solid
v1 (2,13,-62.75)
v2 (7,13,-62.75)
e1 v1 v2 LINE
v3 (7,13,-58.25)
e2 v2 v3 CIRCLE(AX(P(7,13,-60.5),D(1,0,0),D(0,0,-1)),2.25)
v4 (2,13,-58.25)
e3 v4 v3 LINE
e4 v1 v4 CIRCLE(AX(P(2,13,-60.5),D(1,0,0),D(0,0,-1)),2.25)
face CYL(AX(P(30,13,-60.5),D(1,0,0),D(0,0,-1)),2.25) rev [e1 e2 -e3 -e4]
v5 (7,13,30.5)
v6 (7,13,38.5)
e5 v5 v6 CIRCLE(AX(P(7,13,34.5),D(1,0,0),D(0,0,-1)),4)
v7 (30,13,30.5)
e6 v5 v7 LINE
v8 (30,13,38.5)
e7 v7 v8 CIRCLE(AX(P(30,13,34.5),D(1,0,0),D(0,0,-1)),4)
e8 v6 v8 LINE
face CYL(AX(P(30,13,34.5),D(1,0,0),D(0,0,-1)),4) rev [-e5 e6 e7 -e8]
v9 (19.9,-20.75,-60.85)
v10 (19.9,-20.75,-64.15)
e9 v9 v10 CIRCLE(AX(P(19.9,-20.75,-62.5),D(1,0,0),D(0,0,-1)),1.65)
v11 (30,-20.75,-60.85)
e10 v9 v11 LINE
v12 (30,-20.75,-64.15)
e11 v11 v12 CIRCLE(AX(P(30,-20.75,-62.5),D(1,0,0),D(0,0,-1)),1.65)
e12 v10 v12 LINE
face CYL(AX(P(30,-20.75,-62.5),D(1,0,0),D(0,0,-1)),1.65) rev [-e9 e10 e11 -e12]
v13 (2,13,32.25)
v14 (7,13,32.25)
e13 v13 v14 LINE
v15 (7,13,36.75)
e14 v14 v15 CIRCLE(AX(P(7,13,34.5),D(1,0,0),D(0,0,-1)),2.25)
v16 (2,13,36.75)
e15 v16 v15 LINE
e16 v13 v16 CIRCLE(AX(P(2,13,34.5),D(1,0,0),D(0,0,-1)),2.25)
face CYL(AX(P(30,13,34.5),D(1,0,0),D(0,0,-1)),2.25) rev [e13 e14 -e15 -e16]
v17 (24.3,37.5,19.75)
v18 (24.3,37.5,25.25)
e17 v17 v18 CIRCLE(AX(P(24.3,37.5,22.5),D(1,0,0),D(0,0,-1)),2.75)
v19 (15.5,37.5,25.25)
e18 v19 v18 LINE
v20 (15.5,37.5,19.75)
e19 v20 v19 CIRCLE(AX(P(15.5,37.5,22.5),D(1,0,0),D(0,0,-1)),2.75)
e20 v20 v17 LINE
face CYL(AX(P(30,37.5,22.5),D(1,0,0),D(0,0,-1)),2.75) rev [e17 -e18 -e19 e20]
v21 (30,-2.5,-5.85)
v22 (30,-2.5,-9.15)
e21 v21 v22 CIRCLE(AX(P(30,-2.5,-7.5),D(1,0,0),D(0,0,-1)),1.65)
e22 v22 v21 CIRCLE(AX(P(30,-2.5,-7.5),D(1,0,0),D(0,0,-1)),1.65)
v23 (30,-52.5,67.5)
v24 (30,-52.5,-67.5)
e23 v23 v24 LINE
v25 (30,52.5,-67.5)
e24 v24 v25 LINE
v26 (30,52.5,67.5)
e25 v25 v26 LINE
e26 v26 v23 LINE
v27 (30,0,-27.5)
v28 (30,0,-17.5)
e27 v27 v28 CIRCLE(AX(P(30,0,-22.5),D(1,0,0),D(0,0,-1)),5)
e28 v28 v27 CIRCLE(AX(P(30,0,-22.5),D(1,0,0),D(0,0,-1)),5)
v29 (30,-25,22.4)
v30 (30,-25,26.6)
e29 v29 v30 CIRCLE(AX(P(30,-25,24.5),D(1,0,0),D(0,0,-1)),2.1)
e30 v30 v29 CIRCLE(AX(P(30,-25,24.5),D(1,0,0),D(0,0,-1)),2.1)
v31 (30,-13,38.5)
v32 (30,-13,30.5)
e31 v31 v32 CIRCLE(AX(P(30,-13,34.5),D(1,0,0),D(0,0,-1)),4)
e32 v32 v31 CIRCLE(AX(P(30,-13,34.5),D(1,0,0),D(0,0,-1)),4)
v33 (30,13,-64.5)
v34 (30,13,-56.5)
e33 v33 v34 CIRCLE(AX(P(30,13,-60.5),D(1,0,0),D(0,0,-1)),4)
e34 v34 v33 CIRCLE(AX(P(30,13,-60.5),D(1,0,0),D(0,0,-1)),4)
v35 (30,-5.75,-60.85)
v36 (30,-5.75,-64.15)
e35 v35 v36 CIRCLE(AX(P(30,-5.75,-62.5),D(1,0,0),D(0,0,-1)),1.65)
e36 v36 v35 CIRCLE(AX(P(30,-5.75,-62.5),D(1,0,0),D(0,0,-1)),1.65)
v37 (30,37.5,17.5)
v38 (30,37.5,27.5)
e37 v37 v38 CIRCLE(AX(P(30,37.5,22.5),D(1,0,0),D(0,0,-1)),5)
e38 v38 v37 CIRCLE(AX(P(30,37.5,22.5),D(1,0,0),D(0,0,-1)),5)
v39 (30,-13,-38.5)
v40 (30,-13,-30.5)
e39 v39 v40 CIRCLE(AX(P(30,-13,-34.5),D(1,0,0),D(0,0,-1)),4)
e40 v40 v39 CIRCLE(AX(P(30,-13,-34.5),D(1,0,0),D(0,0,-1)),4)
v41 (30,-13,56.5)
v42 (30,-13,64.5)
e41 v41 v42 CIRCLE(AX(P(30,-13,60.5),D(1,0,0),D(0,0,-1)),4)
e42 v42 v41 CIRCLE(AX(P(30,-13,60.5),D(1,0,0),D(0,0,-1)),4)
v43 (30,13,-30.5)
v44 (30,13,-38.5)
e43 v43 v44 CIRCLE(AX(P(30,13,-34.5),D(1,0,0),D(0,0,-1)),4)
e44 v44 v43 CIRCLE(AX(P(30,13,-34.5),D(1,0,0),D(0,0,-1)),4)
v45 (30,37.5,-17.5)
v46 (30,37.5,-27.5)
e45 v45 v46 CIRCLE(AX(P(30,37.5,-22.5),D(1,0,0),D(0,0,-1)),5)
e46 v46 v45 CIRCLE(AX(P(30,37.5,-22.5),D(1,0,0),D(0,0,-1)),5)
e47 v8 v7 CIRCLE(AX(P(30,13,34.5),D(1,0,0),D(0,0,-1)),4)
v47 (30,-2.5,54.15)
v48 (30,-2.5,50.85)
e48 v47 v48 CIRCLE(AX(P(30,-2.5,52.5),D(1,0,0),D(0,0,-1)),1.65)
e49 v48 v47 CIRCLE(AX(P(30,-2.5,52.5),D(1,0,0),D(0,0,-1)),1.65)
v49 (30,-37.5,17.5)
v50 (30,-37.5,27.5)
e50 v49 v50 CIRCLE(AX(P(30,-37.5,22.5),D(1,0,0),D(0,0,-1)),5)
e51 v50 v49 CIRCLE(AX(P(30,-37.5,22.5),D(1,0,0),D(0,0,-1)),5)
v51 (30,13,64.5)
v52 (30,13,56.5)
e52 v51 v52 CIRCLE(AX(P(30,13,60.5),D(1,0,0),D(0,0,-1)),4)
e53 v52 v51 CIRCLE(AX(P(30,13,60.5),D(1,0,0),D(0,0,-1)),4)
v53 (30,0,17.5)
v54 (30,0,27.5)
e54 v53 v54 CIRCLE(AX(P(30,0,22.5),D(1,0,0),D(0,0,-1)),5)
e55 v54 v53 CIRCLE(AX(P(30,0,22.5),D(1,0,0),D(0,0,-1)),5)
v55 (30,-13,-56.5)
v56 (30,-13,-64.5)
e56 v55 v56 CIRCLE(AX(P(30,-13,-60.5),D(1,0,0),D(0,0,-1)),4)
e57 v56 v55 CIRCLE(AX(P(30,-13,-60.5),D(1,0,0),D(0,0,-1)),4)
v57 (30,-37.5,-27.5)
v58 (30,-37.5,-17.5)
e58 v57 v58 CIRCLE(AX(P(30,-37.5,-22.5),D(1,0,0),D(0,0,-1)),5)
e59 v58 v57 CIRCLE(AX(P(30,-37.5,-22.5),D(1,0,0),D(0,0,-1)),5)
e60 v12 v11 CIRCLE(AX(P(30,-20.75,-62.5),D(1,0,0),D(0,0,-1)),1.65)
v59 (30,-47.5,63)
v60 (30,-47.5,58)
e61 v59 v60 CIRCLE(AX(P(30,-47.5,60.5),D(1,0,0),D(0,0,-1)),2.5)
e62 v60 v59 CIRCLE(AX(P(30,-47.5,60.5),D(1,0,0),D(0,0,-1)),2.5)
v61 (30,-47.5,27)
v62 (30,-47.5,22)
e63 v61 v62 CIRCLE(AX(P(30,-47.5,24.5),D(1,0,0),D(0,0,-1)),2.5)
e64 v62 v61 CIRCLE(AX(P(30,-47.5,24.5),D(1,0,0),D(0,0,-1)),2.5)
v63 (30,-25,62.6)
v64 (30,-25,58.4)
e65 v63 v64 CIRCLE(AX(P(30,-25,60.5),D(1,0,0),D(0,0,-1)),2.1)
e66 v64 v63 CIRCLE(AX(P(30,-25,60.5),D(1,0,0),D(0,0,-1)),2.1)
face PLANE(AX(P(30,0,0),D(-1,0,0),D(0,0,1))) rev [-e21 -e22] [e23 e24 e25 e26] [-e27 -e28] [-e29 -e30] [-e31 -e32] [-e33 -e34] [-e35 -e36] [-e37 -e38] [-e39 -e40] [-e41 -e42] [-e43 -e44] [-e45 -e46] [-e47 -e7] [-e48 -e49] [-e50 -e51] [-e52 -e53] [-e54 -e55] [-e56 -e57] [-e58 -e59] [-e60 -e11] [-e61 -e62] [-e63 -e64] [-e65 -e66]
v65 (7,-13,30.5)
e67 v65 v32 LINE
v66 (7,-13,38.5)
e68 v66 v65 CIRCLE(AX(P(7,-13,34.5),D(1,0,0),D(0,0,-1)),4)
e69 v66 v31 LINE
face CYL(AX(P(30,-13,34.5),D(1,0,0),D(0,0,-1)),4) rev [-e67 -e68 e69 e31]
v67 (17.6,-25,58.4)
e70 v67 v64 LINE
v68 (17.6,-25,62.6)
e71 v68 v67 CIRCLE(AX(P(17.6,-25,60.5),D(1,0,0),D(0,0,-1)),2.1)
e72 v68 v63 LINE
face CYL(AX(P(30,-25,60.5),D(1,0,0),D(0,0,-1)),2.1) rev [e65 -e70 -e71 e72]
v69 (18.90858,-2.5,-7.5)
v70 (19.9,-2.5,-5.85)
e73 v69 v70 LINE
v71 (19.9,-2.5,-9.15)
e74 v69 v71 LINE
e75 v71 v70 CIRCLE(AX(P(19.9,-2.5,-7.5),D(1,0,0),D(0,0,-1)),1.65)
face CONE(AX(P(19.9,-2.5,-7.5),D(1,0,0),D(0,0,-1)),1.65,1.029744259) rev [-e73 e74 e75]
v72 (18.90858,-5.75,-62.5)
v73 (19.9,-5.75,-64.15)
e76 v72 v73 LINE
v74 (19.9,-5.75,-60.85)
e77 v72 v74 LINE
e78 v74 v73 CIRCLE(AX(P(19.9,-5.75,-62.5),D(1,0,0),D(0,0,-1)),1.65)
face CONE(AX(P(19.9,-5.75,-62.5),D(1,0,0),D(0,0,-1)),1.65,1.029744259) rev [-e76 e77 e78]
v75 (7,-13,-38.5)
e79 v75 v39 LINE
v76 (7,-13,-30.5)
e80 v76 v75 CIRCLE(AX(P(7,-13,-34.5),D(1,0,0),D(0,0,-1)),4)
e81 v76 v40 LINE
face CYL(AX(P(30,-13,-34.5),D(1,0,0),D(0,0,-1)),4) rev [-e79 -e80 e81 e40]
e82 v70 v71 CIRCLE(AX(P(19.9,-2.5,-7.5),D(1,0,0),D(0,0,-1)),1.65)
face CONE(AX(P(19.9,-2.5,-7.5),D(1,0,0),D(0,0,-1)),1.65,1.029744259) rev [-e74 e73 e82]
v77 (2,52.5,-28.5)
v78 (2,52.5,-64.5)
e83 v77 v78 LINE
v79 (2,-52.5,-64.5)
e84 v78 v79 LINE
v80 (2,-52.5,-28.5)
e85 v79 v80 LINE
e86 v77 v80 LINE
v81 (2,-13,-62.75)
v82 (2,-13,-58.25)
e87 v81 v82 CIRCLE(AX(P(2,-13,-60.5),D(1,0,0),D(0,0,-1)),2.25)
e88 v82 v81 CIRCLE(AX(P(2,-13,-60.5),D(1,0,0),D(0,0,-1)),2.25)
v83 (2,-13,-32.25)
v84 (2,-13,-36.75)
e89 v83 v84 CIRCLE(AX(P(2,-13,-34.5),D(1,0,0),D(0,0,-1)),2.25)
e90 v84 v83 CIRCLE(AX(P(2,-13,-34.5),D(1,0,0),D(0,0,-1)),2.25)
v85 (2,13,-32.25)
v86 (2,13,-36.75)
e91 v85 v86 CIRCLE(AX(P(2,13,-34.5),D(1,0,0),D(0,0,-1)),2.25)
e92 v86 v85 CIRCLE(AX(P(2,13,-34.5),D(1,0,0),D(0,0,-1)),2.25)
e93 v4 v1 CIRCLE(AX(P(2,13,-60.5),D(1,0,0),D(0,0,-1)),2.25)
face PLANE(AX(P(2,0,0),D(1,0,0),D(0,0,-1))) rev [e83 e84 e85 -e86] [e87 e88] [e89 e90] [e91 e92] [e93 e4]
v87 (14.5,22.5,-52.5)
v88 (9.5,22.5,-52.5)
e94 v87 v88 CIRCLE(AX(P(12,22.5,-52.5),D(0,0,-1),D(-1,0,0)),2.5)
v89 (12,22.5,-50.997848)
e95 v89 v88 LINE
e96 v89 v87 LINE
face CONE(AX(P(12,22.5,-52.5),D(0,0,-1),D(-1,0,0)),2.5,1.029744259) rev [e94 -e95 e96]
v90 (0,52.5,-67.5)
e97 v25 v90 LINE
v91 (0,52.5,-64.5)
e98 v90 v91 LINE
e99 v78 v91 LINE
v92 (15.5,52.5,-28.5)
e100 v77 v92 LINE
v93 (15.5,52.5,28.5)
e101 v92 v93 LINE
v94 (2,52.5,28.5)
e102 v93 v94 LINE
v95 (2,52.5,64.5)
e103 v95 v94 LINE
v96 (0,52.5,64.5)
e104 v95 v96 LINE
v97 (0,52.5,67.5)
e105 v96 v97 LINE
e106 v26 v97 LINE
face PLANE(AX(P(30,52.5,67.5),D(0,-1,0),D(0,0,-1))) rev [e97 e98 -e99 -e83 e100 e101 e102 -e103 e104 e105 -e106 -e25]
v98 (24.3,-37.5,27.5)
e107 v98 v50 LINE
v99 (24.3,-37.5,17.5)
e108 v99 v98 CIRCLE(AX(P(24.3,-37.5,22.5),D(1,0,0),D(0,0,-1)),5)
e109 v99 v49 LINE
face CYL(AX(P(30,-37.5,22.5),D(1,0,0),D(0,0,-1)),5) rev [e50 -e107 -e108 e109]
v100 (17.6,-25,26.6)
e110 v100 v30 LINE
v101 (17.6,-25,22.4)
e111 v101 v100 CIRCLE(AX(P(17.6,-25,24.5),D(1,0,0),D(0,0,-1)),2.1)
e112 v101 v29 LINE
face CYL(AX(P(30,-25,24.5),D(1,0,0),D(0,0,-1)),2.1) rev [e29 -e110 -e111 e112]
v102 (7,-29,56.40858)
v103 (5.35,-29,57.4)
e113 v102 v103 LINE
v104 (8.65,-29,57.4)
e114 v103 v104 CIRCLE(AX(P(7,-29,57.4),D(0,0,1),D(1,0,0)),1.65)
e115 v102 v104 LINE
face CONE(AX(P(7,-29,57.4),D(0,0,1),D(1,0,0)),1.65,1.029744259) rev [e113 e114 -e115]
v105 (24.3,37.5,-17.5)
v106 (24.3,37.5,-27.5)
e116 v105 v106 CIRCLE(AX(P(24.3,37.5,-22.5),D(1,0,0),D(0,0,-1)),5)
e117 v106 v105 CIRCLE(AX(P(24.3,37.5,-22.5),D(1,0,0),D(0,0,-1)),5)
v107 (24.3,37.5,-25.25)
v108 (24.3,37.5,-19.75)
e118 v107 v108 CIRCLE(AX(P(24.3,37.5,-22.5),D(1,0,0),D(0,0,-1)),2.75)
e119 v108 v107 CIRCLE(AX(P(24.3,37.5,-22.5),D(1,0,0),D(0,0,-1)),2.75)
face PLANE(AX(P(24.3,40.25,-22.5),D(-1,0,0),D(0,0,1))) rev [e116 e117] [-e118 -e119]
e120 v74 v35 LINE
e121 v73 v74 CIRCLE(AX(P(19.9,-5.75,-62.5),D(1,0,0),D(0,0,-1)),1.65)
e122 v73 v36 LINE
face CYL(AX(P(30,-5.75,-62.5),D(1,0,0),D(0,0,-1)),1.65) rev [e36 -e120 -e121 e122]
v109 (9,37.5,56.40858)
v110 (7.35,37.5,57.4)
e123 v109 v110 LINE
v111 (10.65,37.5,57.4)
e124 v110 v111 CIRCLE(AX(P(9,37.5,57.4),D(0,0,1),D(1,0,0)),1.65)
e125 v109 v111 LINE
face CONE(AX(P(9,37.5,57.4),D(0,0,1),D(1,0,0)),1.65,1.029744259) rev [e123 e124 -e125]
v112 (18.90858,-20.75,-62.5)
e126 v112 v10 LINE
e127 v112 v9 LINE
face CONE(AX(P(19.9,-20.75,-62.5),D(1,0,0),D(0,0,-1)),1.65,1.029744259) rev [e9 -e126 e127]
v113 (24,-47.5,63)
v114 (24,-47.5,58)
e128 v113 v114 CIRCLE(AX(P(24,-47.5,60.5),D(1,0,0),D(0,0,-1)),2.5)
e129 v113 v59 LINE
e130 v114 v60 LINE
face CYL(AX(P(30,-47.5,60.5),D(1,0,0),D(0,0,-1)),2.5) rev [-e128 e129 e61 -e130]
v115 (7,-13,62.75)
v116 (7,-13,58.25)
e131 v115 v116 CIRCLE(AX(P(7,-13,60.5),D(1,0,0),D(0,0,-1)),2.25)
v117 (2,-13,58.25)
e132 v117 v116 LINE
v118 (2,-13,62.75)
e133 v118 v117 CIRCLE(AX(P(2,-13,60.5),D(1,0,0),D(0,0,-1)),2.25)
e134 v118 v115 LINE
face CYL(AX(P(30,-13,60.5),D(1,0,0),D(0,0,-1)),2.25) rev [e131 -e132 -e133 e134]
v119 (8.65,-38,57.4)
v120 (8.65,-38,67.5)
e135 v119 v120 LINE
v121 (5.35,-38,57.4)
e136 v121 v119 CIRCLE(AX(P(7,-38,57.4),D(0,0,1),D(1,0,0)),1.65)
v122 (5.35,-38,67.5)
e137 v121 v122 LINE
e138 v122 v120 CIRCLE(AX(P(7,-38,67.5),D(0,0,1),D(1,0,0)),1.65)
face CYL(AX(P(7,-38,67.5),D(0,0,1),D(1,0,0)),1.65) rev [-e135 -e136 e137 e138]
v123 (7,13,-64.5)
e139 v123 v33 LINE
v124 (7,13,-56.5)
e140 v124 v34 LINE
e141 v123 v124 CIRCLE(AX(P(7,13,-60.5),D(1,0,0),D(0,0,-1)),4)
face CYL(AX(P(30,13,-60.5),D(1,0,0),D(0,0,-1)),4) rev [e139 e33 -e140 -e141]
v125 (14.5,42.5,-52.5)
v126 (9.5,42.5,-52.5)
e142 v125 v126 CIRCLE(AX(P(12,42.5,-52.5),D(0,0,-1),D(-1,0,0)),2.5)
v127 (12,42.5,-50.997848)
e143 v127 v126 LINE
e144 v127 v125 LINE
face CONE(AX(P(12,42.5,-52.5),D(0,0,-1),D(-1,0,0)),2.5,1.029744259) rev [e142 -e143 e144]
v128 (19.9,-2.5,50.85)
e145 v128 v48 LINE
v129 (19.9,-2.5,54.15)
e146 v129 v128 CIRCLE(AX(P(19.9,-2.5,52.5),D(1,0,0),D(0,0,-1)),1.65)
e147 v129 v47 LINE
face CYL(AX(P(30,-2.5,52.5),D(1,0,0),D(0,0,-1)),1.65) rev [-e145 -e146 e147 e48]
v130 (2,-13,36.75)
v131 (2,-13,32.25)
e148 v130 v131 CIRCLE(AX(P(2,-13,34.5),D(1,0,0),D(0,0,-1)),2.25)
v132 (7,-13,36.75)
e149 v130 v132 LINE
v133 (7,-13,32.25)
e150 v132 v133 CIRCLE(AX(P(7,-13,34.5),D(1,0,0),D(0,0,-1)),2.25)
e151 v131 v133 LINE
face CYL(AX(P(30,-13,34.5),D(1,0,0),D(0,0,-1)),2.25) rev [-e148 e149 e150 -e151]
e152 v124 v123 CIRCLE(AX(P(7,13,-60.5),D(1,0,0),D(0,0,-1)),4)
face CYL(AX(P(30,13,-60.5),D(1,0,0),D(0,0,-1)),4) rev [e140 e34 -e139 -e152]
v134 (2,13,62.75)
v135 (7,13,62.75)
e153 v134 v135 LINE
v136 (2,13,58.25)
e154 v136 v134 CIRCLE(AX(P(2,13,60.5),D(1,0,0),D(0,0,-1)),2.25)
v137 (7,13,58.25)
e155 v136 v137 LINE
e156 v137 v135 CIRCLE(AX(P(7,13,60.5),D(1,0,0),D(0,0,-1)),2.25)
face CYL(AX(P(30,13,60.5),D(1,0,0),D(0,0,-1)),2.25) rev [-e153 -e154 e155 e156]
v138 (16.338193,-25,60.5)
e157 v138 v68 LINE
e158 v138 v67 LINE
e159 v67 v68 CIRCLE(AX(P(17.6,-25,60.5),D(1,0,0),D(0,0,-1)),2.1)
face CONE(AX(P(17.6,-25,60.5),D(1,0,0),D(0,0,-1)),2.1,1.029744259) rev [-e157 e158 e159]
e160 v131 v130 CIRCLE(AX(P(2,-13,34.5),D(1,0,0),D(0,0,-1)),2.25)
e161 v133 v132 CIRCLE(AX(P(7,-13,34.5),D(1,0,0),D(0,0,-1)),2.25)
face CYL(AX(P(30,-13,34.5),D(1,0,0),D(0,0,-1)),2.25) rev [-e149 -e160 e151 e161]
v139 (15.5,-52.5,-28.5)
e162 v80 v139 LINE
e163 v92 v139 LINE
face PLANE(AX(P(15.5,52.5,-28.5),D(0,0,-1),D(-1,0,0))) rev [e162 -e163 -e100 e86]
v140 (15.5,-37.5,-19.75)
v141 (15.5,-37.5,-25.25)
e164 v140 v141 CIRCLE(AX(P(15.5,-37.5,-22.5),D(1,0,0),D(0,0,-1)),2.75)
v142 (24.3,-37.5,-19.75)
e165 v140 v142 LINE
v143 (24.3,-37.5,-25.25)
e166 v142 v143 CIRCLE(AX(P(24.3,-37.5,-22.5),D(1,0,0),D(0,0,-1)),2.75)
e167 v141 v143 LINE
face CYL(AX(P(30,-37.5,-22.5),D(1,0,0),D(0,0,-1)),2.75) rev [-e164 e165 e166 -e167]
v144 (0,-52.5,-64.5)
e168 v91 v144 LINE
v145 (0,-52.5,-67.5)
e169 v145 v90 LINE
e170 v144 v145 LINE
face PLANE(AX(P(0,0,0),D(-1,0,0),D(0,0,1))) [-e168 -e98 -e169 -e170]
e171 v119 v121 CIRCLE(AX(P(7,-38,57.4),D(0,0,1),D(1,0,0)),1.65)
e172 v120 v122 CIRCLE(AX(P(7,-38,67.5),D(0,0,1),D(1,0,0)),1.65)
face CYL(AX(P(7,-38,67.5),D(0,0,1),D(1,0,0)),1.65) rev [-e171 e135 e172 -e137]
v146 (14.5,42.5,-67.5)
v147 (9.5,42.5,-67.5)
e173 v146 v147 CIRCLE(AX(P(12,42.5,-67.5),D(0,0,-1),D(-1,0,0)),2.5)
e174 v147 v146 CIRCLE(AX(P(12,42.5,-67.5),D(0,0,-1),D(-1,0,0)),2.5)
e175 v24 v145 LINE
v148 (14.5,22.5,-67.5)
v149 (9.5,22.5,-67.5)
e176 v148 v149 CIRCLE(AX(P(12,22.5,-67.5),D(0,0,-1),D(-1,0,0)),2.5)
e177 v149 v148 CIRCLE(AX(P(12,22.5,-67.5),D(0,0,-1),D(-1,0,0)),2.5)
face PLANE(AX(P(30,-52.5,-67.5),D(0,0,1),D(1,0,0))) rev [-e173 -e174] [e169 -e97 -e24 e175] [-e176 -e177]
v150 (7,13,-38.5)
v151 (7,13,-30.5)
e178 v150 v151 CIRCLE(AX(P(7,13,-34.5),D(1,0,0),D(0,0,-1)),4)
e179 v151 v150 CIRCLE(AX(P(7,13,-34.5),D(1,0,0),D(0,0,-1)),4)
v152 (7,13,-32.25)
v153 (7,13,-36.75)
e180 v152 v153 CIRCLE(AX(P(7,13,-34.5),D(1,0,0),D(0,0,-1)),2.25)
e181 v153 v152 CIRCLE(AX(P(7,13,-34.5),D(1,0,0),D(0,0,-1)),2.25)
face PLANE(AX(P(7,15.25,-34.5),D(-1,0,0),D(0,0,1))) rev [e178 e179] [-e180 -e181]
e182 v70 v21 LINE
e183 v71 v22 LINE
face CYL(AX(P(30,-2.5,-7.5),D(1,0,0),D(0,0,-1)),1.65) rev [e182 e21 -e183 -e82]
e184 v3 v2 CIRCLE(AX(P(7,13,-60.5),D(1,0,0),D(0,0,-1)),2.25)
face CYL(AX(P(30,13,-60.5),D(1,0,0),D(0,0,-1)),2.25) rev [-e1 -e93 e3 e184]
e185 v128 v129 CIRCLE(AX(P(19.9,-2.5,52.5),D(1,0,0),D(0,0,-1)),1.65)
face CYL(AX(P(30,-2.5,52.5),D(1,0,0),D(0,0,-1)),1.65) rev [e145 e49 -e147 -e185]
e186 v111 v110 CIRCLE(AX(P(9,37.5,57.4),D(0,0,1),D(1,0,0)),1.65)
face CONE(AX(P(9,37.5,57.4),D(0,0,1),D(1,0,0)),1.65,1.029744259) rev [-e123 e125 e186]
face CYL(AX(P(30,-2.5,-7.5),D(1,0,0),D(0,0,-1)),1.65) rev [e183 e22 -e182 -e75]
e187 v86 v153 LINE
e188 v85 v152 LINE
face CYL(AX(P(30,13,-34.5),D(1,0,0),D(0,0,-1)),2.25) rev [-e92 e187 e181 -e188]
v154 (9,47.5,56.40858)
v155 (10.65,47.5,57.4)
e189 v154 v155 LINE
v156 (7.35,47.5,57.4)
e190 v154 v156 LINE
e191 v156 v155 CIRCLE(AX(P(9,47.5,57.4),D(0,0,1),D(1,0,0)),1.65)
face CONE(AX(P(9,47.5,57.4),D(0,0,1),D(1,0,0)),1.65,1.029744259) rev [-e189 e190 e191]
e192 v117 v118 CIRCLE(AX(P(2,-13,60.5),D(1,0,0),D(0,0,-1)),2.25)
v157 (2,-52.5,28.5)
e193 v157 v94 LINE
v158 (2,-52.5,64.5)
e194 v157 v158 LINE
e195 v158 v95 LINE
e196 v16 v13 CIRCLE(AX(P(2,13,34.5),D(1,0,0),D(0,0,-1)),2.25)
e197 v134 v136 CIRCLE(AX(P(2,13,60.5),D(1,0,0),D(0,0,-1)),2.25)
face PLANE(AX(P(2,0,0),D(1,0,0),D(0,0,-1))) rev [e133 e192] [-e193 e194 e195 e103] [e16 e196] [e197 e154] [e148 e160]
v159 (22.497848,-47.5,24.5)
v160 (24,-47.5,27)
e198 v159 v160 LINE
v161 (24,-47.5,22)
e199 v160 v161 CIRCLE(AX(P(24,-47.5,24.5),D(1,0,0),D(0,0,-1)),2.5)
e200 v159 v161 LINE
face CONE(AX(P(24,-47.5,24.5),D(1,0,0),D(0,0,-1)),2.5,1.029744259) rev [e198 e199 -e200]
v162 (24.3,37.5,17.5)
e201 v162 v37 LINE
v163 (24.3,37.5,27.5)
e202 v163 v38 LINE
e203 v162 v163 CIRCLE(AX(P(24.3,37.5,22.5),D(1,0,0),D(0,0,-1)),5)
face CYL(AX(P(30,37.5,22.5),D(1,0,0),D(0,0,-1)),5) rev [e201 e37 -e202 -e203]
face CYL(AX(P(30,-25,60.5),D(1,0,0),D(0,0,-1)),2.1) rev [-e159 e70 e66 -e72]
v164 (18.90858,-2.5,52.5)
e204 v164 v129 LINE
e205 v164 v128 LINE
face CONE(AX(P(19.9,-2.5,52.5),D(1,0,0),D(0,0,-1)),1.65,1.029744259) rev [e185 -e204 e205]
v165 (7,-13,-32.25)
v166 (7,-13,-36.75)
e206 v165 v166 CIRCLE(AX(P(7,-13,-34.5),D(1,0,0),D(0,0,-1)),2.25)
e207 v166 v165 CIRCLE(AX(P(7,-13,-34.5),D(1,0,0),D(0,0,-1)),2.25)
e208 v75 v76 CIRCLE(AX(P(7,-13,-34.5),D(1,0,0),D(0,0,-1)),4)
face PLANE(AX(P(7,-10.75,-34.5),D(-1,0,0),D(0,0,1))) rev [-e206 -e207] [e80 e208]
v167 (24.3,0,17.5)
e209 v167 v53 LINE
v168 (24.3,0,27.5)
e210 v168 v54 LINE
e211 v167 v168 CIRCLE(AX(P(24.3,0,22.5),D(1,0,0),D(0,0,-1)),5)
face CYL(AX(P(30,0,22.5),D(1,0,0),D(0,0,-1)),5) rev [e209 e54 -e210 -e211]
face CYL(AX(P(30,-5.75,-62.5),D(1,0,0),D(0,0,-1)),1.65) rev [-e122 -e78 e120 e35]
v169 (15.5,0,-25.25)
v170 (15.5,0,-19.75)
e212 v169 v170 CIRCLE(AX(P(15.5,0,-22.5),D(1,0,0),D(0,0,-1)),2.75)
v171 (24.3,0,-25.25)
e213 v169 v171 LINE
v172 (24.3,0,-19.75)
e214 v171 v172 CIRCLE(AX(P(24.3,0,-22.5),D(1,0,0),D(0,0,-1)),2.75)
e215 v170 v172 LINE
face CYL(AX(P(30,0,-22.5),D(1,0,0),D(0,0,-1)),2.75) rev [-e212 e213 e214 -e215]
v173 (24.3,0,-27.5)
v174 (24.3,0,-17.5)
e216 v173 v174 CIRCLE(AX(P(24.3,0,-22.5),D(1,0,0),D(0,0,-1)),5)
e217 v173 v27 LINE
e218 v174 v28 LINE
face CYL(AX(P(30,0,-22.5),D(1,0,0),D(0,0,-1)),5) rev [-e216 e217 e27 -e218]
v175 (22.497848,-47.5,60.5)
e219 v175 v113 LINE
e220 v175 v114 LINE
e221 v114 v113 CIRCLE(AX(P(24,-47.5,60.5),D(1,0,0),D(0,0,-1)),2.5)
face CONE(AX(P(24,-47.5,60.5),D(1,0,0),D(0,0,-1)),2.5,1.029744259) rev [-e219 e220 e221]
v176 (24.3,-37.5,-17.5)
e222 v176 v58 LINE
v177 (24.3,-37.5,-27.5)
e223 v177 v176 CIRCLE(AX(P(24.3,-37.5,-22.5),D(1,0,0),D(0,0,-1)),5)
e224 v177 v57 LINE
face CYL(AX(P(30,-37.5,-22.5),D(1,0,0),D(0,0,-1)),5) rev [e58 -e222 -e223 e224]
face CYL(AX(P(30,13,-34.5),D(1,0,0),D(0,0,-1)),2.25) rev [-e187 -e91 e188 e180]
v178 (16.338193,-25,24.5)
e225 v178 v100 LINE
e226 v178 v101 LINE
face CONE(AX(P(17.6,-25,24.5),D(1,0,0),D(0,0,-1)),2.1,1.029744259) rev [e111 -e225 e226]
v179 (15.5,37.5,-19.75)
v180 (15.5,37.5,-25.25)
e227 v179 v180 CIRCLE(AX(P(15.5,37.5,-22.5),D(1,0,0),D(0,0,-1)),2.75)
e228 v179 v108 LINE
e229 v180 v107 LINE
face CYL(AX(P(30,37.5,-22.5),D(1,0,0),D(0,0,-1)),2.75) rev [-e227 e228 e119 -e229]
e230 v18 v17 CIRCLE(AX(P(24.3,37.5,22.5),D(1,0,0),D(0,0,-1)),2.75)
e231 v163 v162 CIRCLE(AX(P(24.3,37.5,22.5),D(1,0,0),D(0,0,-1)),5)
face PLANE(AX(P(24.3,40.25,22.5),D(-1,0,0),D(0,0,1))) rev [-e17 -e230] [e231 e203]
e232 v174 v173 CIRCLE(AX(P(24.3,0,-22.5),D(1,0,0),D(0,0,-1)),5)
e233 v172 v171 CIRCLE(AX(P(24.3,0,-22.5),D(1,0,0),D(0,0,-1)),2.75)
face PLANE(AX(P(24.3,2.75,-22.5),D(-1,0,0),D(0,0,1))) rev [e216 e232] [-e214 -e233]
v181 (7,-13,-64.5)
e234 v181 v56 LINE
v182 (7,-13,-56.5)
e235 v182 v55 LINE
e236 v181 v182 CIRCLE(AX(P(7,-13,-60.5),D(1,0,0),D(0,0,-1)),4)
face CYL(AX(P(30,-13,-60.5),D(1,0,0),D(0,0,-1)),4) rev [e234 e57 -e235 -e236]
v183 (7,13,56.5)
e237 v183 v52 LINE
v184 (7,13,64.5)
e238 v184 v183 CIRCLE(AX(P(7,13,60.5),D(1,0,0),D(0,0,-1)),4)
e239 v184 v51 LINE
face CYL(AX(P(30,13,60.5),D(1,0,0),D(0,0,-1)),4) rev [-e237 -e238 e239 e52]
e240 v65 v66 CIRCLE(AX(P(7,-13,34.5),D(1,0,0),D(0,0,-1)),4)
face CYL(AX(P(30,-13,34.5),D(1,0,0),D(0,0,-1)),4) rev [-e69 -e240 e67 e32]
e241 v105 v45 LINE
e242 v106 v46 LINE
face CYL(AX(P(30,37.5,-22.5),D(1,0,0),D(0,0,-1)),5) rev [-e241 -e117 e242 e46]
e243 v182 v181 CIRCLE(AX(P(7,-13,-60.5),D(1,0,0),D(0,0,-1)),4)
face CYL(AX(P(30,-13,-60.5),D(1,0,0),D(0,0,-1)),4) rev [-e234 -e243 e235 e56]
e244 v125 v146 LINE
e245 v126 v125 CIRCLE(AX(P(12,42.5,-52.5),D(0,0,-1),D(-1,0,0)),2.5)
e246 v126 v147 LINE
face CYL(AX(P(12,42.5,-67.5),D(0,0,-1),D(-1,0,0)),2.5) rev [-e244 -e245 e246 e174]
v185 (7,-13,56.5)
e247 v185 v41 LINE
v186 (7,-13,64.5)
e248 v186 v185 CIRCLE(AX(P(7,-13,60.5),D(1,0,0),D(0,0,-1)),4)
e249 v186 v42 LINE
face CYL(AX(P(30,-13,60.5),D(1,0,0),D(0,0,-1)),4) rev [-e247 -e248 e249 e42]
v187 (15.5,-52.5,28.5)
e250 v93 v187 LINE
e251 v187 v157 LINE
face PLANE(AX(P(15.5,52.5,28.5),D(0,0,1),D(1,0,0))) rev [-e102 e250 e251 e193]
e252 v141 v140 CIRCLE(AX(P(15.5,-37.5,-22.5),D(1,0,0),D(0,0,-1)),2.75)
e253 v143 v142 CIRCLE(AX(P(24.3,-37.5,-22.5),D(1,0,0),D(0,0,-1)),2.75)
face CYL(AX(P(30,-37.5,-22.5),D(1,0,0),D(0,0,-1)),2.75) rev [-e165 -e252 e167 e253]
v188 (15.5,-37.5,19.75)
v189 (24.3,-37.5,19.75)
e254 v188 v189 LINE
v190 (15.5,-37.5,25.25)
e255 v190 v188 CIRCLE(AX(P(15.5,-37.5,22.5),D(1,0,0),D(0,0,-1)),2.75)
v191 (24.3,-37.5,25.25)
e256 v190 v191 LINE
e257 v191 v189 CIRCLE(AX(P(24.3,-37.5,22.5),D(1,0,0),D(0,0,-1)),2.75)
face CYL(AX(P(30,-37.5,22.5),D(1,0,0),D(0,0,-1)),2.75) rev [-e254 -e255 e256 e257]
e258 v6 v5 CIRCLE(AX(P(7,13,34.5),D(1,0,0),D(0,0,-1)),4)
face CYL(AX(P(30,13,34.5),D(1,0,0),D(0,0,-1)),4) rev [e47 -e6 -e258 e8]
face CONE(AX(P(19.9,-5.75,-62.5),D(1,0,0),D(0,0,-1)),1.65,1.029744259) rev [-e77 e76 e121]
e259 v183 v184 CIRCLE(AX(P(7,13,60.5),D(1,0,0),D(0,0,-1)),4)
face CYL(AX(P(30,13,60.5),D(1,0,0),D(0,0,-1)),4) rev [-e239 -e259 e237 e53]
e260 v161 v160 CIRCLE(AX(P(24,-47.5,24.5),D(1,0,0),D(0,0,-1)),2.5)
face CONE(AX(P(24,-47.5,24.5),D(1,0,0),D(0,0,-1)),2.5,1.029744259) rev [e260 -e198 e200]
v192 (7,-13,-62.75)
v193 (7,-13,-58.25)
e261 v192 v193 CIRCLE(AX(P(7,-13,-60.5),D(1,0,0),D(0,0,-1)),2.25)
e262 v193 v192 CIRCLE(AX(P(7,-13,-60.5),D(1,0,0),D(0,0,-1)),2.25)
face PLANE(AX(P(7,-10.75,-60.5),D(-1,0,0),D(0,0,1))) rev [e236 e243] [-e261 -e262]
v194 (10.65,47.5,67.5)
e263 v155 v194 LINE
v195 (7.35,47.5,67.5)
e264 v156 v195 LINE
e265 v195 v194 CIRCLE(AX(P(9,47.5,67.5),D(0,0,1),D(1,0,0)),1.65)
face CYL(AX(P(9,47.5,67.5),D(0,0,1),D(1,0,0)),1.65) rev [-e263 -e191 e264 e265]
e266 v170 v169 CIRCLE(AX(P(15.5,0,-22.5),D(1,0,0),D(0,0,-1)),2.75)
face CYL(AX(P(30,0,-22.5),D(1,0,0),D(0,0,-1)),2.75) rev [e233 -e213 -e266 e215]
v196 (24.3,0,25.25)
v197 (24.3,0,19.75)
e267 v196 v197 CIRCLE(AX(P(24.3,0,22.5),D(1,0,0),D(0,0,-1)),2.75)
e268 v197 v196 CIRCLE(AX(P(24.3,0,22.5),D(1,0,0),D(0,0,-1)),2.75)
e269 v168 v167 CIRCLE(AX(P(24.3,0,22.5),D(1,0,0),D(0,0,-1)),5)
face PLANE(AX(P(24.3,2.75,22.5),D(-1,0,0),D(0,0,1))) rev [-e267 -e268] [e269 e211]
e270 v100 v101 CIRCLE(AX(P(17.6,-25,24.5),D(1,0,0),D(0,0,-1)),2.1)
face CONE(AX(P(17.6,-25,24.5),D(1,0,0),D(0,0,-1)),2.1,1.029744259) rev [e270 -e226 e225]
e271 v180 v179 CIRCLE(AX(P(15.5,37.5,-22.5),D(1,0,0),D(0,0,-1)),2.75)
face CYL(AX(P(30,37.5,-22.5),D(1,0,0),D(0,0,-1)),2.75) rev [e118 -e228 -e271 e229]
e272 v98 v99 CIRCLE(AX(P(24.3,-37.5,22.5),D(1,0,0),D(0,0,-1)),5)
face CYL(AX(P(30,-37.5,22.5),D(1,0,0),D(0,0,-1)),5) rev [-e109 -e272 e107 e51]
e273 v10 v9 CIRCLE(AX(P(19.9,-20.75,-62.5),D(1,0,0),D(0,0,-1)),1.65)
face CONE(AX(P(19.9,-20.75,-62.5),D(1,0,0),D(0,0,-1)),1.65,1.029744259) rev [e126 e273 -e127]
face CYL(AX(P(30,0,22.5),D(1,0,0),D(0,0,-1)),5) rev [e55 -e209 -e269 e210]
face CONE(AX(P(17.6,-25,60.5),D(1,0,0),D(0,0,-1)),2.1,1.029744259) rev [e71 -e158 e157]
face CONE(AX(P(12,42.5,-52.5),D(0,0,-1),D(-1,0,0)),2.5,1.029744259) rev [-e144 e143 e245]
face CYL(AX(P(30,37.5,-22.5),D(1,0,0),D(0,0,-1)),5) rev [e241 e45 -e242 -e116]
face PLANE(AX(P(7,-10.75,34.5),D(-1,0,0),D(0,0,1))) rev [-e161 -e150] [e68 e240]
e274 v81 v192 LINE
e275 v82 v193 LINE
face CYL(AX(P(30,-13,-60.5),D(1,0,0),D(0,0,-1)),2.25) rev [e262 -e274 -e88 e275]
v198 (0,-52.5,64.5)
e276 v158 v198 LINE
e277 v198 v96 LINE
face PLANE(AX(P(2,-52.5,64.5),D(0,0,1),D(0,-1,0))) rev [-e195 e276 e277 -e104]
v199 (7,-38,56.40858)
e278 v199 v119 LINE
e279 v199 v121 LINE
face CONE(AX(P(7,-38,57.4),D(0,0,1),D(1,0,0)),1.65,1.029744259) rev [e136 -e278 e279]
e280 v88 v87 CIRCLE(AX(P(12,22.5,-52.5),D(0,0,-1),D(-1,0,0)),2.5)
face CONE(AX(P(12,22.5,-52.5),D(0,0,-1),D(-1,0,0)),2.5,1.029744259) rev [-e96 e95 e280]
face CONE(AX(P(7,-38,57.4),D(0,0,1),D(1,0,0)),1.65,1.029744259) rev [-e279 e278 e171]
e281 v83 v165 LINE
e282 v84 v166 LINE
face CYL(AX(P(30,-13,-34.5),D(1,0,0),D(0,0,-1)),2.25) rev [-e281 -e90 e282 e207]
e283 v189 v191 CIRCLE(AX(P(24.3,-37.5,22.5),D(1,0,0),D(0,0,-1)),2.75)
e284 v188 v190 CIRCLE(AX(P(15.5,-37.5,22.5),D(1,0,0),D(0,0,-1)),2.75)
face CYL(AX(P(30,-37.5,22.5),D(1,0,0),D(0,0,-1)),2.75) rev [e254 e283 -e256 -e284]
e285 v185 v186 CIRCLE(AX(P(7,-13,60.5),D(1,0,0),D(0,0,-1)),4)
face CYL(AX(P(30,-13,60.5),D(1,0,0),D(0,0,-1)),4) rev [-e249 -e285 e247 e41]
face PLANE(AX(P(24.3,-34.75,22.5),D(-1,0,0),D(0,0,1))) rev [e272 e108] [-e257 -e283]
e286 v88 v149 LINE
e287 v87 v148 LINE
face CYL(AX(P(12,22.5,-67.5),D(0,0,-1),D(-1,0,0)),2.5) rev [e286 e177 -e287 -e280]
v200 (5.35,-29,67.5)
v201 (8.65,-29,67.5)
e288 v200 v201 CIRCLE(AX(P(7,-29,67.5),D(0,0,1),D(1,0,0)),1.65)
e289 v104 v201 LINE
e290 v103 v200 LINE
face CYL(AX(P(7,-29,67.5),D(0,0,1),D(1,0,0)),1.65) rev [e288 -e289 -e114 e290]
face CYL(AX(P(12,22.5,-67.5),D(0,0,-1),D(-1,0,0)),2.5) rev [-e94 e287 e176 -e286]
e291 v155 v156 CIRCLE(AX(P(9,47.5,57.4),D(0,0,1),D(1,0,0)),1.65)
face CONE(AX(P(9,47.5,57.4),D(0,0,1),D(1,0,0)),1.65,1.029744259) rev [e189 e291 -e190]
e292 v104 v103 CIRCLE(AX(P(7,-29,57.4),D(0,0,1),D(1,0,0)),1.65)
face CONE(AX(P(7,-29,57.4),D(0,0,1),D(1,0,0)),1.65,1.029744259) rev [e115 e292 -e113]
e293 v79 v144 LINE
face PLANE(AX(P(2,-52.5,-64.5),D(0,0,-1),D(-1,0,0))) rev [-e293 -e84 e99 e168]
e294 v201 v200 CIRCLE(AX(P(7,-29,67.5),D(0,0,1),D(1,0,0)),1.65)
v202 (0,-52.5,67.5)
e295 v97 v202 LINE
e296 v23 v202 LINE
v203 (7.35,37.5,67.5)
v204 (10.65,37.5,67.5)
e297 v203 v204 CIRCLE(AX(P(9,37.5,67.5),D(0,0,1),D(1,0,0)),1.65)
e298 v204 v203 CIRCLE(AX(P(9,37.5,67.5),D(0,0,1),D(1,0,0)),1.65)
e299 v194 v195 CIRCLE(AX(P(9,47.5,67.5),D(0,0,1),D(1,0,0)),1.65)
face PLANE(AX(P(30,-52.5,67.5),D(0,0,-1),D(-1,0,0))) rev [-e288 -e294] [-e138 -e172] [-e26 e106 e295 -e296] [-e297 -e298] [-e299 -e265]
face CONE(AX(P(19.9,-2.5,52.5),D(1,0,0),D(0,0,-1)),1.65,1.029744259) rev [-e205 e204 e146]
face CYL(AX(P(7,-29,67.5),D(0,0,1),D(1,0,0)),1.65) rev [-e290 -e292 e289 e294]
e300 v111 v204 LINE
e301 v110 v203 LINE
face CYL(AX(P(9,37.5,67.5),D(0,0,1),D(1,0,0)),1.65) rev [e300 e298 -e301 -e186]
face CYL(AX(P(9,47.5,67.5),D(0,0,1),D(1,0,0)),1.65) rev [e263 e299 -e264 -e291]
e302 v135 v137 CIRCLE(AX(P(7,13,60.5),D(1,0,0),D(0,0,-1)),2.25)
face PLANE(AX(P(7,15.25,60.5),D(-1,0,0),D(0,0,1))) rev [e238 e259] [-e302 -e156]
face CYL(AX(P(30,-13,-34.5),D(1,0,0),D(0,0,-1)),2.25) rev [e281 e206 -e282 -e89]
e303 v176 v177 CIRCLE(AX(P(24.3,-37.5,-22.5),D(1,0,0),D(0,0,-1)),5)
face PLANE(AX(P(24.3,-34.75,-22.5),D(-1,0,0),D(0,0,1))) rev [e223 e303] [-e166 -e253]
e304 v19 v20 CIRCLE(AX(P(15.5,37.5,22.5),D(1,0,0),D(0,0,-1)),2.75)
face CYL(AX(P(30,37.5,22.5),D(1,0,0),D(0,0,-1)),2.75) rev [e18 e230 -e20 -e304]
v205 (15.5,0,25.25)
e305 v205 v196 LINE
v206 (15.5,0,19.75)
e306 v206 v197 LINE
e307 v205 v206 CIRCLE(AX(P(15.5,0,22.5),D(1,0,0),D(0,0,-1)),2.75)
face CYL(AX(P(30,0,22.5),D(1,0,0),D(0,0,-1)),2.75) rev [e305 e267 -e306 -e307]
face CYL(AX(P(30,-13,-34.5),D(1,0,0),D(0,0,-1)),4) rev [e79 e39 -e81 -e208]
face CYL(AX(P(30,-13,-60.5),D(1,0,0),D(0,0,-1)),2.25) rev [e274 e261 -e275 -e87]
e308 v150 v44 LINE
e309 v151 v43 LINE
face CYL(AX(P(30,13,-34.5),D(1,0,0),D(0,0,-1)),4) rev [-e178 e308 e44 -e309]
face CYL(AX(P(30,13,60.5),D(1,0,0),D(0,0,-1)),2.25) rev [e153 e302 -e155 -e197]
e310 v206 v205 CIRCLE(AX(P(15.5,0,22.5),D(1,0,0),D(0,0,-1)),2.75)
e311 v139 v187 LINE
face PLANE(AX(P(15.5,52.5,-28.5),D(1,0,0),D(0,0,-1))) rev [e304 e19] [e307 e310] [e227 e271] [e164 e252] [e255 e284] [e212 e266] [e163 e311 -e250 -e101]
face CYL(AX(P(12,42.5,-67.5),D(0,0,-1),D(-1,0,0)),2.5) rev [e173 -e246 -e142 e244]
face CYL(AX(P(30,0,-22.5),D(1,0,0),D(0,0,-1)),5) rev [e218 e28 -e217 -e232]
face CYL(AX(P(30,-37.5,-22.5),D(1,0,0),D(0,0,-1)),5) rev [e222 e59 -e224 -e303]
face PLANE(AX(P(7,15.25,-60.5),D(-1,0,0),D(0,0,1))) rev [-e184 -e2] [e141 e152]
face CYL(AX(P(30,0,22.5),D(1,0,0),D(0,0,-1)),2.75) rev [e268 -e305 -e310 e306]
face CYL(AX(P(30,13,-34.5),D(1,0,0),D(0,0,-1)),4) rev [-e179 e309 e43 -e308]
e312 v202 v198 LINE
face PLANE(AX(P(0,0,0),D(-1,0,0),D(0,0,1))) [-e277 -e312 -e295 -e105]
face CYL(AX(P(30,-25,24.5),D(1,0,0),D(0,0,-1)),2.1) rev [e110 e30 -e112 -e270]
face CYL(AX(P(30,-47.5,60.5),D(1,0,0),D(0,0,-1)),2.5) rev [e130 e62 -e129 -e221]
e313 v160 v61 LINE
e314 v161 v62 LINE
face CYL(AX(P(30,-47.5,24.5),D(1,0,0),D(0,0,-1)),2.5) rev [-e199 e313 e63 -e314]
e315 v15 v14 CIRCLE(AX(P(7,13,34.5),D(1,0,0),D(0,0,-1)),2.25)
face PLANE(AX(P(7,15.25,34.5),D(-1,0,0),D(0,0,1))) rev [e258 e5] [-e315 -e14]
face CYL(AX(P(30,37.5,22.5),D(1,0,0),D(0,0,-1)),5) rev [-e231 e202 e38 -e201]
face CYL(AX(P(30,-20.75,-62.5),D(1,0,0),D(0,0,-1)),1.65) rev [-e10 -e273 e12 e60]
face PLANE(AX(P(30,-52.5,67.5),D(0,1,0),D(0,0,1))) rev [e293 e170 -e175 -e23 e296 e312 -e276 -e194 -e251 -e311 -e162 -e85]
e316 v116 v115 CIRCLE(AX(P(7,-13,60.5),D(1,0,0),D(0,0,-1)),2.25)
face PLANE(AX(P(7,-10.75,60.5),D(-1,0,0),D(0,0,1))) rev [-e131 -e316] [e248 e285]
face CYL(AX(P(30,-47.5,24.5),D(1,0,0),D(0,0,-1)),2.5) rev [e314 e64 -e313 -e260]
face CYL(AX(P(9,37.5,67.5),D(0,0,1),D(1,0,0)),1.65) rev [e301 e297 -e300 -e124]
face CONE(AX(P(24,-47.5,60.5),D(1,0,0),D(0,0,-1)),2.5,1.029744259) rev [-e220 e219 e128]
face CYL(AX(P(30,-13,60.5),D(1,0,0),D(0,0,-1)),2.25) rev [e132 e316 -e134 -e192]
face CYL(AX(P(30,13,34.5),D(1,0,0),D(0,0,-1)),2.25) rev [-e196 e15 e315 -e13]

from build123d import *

# Parameters (mm, degrees)
SKETCH1_W                                            = 135
SKETCH1_H                                            = 105
BOSS_EXTRUDE1_DEPTH                                  = 30
SKETCH2_W                                            = 15.5
SKETCH2_H                                            = 57
CUT_EXTRUDE1_DEPTH                                   = 129.379320765
SKETCH3_W                                            = 129
SKETCH3_H                                            = 105
CUT_EXTRUDE2_DEPTH                                   = 2
CBORE_FOR_M5_HEXAGON_SOCKET_HEAD_CAP_SCR_D           = 5.5
CBORE_FOR_M5_HEXAGON_SOCKET_HEAD_CAP_SCR_CBORE_D     = 10
CBORE_FOR_M5_HEXAGON_SOCKET_HEAD_CAP_SCR_CBORE_DEPTH = 5.7
CBORE_FOR_M4_HEXAGON_SOCKET_HEAD_CAP_SCR_D           = 4.5
CBORE_FOR_M4_HEXAGON_SOCKET_HEAD_CAP_SCR_CBORE_D     = 8
CBORE_FOR_M4_HEXAGON_SOCKET_HEAD_CAP_SCR_CBORE_DEPTH = 23
M4_TAPPED_HOLE1_D                                    = 3.3
M4_TAPPED_HOLE1_DEPTH                                = 10.1
M4_TAPPED_HOLE1_TIP                                  = 0.991420021
M6_TAPPED_HOLE1_D                                    = 5
M6_TAPPED_HOLE1_DEPTH                                = 15
M6_TAPPED_HOLE1_TIP                                  = 1.502151548
M4_TAPPED_HOLE2_D                                    = 3.3
M4_TAPPED_HOLE2_DEPTH                                = 10.1
M4_TAPPED_HOLE2_TIP                                  = 0.991420021
M4_TAPPED_HOLE3_D                                    = 3.3
M4_TAPPED_HOLE3_DEPTH                                = 10.1
M4_TAPPED_HOLE3_TIP                                  = 0.991420021
M5_TAPPED_HOLE1_D                                    = 4.2
M5_TAPPED_HOLE1_DEPTH                                = 12.4
M5_TAPPED_HOLE1_TIP                                  = 1.2618073
F_5_0MM_DOWEL_HOLE1_D                                = 5
F_5_0MM_DOWEL_HOLE1_DEPTH                            = 6
F_5_0MM_DOWEL_HOLE1_TIP                              = 1.502151548
M4_TAPPED_HOLE4_D                                    = 3.3
M4_TAPPED_HOLE4_DEPTH                                = 10.1
M4_TAPPED_HOLE4_TIP                                  = 0.991420021


with BuildPart() as part:
    # Sketch1 → Boss-Extrude1 (new body)
    with BuildSketch(Plane(origin=(0, 0, 0), x_dir=(0, 0, -1), z_dir=(1, 0, 0))):
        Rectangle(SKETCH1_W, SKETCH1_H)
    extrude(amount=BOSS_EXTRUDE1_DEPTH)

    # Sketch2 → Cut-Extrude1 (cut, through all)
    with BuildSketch(Plane.XZ.offset(52.5)):
        with Locations((7.75, 0)):
            Rectangle(SKETCH2_W, SKETCH2_H)
    extrude(amount=-CUT_EXTRUDE1_DEPTH, mode=Mode.SUBTRACT)

    # Sketch3 → Cut-Extrude2 (cut)
    with BuildSketch(Plane.ZY):
        Rectangle(SKETCH3_W, SKETCH3_H)
    extrude(amount=-CUT_EXTRUDE2_DEPTH, mode=Mode.SUBTRACT)

    # CBORE for M5 Hexagon socket head cap screws1 (through all)
    with Locations(Plane(origin=(30, 0, 0), x_dir=(0, 0, -1), z_dir=(1, 0, 0))):
        with Locations((22.5, -37.5), (22.5, 37.5), (-22.5, 37.5), (-22.5, 0), (22.5, 0), (-22.5, -37.5)):
            CounterBoreHole(CBORE_FOR_M5_HEXAGON_SOCKET_HEAD_CAP_SCR_D / 2, CBORE_FOR_M5_HEXAGON_SOCKET_HEAD_CAP_SCR_CBORE_D / 2, CBORE_FOR_M5_HEXAGON_SOCKET_HEAD_CAP_SCR_CBORE_DEPTH)

    # CBORE for M4 Hexagon socket head cap screws1 (through all)
    with Locations(Plane(origin=(30, 0, 0), x_dir=(0, 0, -1), z_dir=(1, 0, 0))):
        with Locations((34.5, 13), (60.5, 13), (60.5, -13), (34.5, -13)):
            cbore_for_m4_hexagon_socket_head_cap_scr = CounterBoreHole(CBORE_FOR_M4_HEXAGON_SOCKET_HEAD_CAP_SCR_D / 2, CBORE_FOR_M4_HEXAGON_SOCKET_HEAD_CAP_SCR_CBORE_D / 2, CBORE_FOR_M4_HEXAGON_SOCKET_HEAD_CAP_SCR_CBORE_DEPTH)

    # Mirror1: CBORE for M4 Hexagon socket head cap screws1 across plane
    add(cbore_for_m4_hexagon_socket_head_cap_scr.mirror(Plane.XY), mode=Mode.SUBTRACT)

    # M4 Tapped Hole1
    with Locations(Plane(origin=(30, 0, 0), x_dir=(0, 0, -1), z_dir=(1, 0, 0))):
        with Locations((62.5, -5.75), (62.5, -20.75)):
            Hole(M4_TAPPED_HOLE1_D / 2, depth=M4_TAPPED_HOLE1_DEPTH)
            with Locations((0, 0, -(M4_TAPPED_HOLE1_DEPTH + M4_TAPPED_HOLE1_TIP / 2))):  # 118° drill point
                Cone(0, M4_TAPPED_HOLE1_D / 2, M4_TAPPED_HOLE1_TIP, mode=Mode.SUBTRACT)

    # M6 Tapped Hole1
    with Locations(Plane(origin=(0, 0, -67.5), x_dir=(-1, 0, 0), z_dir=(0, 0, -1))):
        with Locations((-12, 42.5), (-12, 22.5)):
            Hole(M6_TAPPED_HOLE1_D / 2, depth=M6_TAPPED_HOLE1_DEPTH)
            with Locations((0, 0, -(M6_TAPPED_HOLE1_DEPTH + M6_TAPPED_HOLE1_TIP / 2))):  # 118° drill point
                Cone(0, M6_TAPPED_HOLE1_D / 2, M6_TAPPED_HOLE1_TIP, mode=Mode.SUBTRACT)

    # M4 Tapped Hole2
    with Locations(Plane.XY.offset(67.5)):
        with Locations((9, 37.5), (9, 47.5)):
            Hole(M4_TAPPED_HOLE2_D / 2, depth=M4_TAPPED_HOLE2_DEPTH)
            with Locations((0, 0, -(M4_TAPPED_HOLE2_DEPTH + M4_TAPPED_HOLE2_TIP / 2))):  # 118° drill point
                Cone(0, M4_TAPPED_HOLE2_D / 2, M4_TAPPED_HOLE2_TIP, mode=Mode.SUBTRACT)

    # M4 Tapped Hole3
    with Locations(Plane.XY.offset(67.5)):
        with Locations((7, -29), (7, -38)):
            Hole(M4_TAPPED_HOLE3_D / 2, depth=M4_TAPPED_HOLE3_DEPTH)
            with Locations((0, 0, -(M4_TAPPED_HOLE3_DEPTH + M4_TAPPED_HOLE3_TIP / 2))):  # 118° drill point
                Cone(0, M4_TAPPED_HOLE3_D / 2, M4_TAPPED_HOLE3_TIP, mode=Mode.SUBTRACT)

    # M5 Tapped Hole1
    with Locations(Plane(origin=(30, 0, 0), x_dir=(0, 0, -1), z_dir=(1, 0, 0))):
        with Locations((-24.5, -25), (-60.5, -25)):
            Hole(M5_TAPPED_HOLE1_D / 2, depth=M5_TAPPED_HOLE1_DEPTH)
            with Locations((0, 0, -(M5_TAPPED_HOLE1_DEPTH + M5_TAPPED_HOLE1_TIP / 2))):  # 118° drill point
                Cone(0, M5_TAPPED_HOLE1_D / 2, M5_TAPPED_HOLE1_TIP, mode=Mode.SUBTRACT)

    # Ø5.0mm Dowel Hole1
    with Locations(Plane(origin=(30, 0, 0), x_dir=(0, 0, -1), z_dir=(1, 0, 0))):
        with Locations((-24.5, -47.5), (-60.5, -47.5)):
            Hole(F_5_0MM_DOWEL_HOLE1_D / 2, depth=F_5_0MM_DOWEL_HOLE1_DEPTH)
            with Locations((0, 0, -(F_5_0MM_DOWEL_HOLE1_DEPTH + F_5_0MM_DOWEL_HOLE1_TIP / 2))):  # 118° drill point
                Cone(0, F_5_0MM_DOWEL_HOLE1_D / 2, F_5_0MM_DOWEL_HOLE1_TIP, mode=Mode.SUBTRACT)

    # M4 Tapped Hole4
    with Locations(Plane(origin=(30, 0, 0), x_dir=(0, 0, -1), z_dir=(1, 0, 0))):
        with Locations((7.5, -2.5), (-52.5, -2.5)):
            Hole(M4_TAPPED_HOLE4_D / 2, depth=M4_TAPPED_HOLE4_DEPTH)
            with Locations((0, 0, -(M4_TAPPED_HOLE4_DEPTH + M4_TAPPED_HOLE4_TIP / 2))):  # 118° drill point
                Cone(0, M4_TAPPED_HOLE4_D / 2, M4_TAPPED_HOLE4_TIP, mode=Mode.SUBTRACT)


solid = part.part
